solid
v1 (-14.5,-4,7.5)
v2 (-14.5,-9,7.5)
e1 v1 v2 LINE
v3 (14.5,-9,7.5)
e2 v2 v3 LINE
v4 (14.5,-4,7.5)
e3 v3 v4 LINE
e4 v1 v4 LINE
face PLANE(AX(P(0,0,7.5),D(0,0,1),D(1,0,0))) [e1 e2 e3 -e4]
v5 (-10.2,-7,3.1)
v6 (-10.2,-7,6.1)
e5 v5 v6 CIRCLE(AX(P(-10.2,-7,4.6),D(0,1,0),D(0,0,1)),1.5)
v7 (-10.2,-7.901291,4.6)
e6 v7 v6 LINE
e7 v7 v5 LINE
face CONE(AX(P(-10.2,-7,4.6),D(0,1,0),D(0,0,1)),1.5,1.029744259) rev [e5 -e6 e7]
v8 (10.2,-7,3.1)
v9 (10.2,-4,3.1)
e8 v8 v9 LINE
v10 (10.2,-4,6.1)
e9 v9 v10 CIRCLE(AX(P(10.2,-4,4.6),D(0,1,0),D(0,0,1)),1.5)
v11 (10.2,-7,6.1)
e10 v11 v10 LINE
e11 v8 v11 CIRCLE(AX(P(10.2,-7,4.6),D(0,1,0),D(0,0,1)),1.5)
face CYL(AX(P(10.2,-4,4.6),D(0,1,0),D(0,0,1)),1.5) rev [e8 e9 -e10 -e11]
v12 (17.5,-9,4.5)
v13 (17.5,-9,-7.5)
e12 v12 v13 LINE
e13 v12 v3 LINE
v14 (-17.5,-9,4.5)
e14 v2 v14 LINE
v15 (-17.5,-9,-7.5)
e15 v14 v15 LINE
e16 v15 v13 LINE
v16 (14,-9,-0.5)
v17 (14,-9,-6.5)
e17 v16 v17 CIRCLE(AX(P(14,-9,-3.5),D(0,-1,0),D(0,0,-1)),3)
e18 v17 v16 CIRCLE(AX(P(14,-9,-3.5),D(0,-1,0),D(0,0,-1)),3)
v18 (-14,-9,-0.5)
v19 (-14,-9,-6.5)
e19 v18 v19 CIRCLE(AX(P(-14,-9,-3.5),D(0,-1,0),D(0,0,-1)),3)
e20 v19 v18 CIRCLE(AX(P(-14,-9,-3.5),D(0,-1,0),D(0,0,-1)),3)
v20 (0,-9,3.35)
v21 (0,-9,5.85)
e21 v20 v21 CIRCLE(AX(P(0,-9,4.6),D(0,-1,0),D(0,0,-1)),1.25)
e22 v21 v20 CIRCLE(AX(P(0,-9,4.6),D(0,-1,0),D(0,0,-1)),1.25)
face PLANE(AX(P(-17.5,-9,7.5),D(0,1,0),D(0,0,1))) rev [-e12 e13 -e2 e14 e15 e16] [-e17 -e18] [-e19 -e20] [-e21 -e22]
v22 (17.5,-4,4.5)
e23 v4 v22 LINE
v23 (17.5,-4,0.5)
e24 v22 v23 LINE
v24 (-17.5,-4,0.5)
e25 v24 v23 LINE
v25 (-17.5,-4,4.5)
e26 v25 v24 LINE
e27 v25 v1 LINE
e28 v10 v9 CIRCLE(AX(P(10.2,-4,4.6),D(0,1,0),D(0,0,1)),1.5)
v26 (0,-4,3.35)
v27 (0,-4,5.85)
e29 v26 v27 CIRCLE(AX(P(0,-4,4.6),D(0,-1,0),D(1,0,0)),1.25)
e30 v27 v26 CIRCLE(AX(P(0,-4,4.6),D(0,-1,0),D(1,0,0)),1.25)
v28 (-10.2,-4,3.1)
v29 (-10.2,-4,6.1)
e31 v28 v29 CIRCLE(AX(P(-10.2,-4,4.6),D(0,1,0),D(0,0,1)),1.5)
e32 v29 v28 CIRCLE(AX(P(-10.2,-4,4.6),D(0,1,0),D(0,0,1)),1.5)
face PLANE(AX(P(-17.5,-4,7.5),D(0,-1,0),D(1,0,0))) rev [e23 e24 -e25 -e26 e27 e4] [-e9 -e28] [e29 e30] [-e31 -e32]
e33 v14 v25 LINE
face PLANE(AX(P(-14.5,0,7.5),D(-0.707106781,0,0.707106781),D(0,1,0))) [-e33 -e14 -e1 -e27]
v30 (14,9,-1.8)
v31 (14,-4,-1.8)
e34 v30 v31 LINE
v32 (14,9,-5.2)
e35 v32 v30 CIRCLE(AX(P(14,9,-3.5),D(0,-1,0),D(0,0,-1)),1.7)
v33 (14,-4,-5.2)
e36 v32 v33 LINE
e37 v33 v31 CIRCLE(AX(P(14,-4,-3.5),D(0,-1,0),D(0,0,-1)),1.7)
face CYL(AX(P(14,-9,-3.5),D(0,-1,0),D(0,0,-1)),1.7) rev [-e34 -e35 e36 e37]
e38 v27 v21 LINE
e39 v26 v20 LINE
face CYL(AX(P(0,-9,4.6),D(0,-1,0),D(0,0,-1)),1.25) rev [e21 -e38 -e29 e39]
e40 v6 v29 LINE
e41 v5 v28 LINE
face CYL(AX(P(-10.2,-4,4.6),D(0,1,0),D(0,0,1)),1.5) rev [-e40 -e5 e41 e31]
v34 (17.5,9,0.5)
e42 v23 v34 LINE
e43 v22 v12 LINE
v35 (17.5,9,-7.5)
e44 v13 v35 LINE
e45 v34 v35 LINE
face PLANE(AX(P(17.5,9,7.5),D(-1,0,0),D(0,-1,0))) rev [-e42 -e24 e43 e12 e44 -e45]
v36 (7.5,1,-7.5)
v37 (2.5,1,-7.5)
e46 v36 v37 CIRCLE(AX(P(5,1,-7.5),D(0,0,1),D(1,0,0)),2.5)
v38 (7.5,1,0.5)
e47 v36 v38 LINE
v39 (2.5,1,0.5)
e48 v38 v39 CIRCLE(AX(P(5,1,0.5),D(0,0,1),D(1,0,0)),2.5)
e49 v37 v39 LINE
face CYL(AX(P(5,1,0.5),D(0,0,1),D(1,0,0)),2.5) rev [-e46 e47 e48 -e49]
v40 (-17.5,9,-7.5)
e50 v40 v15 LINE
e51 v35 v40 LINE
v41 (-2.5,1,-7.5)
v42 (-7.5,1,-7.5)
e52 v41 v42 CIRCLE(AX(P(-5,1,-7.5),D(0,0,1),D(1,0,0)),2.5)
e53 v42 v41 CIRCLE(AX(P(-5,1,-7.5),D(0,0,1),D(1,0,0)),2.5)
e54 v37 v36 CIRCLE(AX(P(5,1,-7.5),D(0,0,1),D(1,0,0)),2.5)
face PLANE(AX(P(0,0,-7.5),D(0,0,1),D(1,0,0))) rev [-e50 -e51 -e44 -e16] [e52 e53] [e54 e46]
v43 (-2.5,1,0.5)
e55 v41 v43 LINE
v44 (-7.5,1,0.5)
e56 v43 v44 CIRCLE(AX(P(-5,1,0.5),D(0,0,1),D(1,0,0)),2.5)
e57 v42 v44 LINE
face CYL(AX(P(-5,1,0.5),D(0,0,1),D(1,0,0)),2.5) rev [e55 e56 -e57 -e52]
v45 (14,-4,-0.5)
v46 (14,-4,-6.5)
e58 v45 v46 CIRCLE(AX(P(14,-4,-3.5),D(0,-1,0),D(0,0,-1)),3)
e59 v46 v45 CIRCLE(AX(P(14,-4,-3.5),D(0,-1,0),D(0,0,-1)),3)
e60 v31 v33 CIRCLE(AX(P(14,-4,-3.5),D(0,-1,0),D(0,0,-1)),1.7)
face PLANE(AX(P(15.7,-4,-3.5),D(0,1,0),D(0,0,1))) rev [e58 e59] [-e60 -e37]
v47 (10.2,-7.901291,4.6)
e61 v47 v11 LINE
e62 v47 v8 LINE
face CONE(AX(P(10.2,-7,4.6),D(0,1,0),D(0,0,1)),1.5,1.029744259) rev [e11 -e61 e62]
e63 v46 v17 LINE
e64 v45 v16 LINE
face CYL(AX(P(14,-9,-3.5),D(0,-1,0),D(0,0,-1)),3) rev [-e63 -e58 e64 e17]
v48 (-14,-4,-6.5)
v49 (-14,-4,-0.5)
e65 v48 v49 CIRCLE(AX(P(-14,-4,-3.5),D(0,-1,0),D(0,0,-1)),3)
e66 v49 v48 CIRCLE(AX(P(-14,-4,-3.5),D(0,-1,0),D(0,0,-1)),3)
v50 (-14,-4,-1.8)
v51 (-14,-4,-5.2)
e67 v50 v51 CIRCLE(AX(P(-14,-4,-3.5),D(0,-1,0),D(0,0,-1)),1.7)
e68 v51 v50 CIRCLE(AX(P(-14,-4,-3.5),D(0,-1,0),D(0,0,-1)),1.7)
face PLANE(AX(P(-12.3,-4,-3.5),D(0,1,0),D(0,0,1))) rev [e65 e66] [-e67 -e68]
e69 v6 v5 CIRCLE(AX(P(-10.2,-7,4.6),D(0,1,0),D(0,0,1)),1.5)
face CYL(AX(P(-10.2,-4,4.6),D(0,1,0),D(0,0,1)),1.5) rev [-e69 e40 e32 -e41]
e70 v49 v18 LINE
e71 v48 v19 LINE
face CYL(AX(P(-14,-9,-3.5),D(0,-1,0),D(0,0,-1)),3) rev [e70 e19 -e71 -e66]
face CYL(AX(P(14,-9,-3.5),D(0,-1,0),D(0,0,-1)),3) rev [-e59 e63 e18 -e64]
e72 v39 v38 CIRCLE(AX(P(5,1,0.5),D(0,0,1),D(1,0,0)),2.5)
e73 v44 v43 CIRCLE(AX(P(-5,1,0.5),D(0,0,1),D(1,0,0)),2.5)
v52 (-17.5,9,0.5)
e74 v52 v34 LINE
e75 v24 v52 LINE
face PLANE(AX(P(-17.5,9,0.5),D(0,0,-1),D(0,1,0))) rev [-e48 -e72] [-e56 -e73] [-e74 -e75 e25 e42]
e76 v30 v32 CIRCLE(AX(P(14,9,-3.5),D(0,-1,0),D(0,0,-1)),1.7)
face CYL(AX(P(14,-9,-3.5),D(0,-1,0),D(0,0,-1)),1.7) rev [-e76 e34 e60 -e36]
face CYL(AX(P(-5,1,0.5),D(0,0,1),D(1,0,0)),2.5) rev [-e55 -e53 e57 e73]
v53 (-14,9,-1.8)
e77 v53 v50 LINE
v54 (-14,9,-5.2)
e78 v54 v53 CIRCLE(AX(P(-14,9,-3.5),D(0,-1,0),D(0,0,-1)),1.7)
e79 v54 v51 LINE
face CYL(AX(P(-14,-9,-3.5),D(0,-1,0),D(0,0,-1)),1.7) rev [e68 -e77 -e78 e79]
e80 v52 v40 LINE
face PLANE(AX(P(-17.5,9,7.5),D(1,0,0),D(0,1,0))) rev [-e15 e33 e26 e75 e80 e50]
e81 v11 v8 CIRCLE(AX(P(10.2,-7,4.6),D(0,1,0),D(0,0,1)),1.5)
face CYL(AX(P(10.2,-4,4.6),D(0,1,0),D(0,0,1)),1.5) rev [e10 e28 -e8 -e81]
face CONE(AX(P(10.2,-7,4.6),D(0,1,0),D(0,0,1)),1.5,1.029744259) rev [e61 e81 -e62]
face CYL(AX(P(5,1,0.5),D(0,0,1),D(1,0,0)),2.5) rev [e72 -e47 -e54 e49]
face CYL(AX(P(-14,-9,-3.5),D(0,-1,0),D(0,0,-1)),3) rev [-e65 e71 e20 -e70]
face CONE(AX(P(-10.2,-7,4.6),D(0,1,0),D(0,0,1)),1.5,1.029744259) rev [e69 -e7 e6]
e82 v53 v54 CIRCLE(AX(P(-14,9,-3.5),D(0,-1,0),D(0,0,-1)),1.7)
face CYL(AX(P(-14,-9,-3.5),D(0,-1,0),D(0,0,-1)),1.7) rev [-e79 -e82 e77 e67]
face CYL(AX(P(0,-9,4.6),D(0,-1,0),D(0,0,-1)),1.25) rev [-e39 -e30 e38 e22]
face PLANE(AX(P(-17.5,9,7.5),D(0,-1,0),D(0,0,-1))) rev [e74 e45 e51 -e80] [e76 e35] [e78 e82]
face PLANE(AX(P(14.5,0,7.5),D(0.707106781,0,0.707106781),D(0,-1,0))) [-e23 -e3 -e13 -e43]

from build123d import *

# Parameters (mm, degrees)
SKETCH1_W                                            = 35
SKETCH1_H                                            = 18
BOSS_EXTRUDE1_DEPTH                                  = 7.5
SKETCH2_W                                            = 7
SKETCH2_H                                            = 13
CUT_EXTRUDE1_DEPTH                                   = 37.908671068
F_5_0_5_DIAMETER_HOLE1_D                             = 5
F_3_0_3_DIAMETER_HOLE2_D                             = 3
F_3_0_3_DIAMETER_HOLE2_DEPTH                         = 3
F_3_0_3_DIAMETER_HOLE2_TIP                           = 0.901290929
M3_TAPPED_HOLE1_D                                    = 2.5
HOLE_SIZE_PER_SOCKET_HEAD_CAP_SCREW_TYPE_D           = 3.4
HOLE_SIZE_PER_SOCKET_HEAD_CAP_SCREW_TYPE_CBORE_D     = 6
HOLE_SIZE_PER_SOCKET_HEAD_CAP_SCREW_TYPE_CBORE_DEPTH = 5
CHAMFER1_SIZE                                        = 3


with BuildPart() as part:
    # Sketch1 → Boss-Extrude1 (new, symmetric)
    with BuildSketch(Plane.XY):
        Rectangle(SKETCH1_W, SKETCH1_H)
    extrude(amount=BOSS_EXTRUDE1_DEPTH, both=True)

    # Sketch2 → Cut-Extrude1 (cut, through all)
    with BuildSketch(Plane(origin=(17.5, 0, 0), x_dir=(0, 0, -1), z_dir=(1, 0, 0))):
        with Locations((-4, 2.5)):
            Rectangle(SKETCH2_W, SKETCH2_H)
    extrude(amount=-CUT_EXTRUDE1_DEPTH, mode=Mode.SUBTRACT)

    # Ø5.0 (5) Diameter Hole1 (through all)
    with Locations(Plane.XY.offset(0.5)):
        with Locations((-5, 1), (5, 1)):
            Hole(F_5_0_5_DIAMETER_HOLE1_D / 2)

    # Ø3.0 (3) Diameter Hole2
    with Locations(Plane(origin=(0, -4, 0), x_dir=(1, 0, 0), z_dir=(0, 1, 0))):
        with Locations((10.2, -4.6), (-10.2, -4.6)):
            Hole(F_3_0_3_DIAMETER_HOLE2_D / 2, depth=F_3_0_3_DIAMETER_HOLE2_DEPTH)
            with Locations((0, 0, -(F_3_0_3_DIAMETER_HOLE2_DEPTH + F_3_0_3_DIAMETER_HOLE2_TIP / 2))):  # 118° drill point
                Cone(0, F_3_0_3_DIAMETER_HOLE2_D / 2, F_3_0_3_DIAMETER_HOLE2_TIP, mode=Mode.SUBTRACT)

    # M3 Tapped Hole1 (through all)
    with Locations(Plane(origin=(0, -9, 0), x_dir=(-1, 0, 0), z_dir=(0, -1, 0))):
        with Locations((0, -4.6)):
            Hole(M3_TAPPED_HOLE1_D / 2)

    # Hole size per socket head cap screw type1 (through all)
    with Locations(Plane(origin=(0, -9, 0), x_dir=(-1, 0, 0), z_dir=(0, -1, 0))):
        with Locations((14, 3.5), (-14, 3.5)):
            CounterBoreHole(HOLE_SIZE_PER_SOCKET_HEAD_CAP_SCREW_TYPE_D / 2, HOLE_SIZE_PER_SOCKET_HEAD_CAP_SCREW_TYPE_CBORE_D / 2, HOLE_SIZE_PER_SOCKET_HEAD_CAP_SCREW_TYPE_CBORE_DEPTH)

    # Chamfer1
    chamfer1_edges = [part.edges().sort_by_distance(p)[0] for p in [
        (-17.5, -6.5, 7.5),
        (17.5, -6.5, 7.5),
    ]]
    chamfer(chamfer1_edges, length=CHAMFER1_SIZE)


solid = part.part
